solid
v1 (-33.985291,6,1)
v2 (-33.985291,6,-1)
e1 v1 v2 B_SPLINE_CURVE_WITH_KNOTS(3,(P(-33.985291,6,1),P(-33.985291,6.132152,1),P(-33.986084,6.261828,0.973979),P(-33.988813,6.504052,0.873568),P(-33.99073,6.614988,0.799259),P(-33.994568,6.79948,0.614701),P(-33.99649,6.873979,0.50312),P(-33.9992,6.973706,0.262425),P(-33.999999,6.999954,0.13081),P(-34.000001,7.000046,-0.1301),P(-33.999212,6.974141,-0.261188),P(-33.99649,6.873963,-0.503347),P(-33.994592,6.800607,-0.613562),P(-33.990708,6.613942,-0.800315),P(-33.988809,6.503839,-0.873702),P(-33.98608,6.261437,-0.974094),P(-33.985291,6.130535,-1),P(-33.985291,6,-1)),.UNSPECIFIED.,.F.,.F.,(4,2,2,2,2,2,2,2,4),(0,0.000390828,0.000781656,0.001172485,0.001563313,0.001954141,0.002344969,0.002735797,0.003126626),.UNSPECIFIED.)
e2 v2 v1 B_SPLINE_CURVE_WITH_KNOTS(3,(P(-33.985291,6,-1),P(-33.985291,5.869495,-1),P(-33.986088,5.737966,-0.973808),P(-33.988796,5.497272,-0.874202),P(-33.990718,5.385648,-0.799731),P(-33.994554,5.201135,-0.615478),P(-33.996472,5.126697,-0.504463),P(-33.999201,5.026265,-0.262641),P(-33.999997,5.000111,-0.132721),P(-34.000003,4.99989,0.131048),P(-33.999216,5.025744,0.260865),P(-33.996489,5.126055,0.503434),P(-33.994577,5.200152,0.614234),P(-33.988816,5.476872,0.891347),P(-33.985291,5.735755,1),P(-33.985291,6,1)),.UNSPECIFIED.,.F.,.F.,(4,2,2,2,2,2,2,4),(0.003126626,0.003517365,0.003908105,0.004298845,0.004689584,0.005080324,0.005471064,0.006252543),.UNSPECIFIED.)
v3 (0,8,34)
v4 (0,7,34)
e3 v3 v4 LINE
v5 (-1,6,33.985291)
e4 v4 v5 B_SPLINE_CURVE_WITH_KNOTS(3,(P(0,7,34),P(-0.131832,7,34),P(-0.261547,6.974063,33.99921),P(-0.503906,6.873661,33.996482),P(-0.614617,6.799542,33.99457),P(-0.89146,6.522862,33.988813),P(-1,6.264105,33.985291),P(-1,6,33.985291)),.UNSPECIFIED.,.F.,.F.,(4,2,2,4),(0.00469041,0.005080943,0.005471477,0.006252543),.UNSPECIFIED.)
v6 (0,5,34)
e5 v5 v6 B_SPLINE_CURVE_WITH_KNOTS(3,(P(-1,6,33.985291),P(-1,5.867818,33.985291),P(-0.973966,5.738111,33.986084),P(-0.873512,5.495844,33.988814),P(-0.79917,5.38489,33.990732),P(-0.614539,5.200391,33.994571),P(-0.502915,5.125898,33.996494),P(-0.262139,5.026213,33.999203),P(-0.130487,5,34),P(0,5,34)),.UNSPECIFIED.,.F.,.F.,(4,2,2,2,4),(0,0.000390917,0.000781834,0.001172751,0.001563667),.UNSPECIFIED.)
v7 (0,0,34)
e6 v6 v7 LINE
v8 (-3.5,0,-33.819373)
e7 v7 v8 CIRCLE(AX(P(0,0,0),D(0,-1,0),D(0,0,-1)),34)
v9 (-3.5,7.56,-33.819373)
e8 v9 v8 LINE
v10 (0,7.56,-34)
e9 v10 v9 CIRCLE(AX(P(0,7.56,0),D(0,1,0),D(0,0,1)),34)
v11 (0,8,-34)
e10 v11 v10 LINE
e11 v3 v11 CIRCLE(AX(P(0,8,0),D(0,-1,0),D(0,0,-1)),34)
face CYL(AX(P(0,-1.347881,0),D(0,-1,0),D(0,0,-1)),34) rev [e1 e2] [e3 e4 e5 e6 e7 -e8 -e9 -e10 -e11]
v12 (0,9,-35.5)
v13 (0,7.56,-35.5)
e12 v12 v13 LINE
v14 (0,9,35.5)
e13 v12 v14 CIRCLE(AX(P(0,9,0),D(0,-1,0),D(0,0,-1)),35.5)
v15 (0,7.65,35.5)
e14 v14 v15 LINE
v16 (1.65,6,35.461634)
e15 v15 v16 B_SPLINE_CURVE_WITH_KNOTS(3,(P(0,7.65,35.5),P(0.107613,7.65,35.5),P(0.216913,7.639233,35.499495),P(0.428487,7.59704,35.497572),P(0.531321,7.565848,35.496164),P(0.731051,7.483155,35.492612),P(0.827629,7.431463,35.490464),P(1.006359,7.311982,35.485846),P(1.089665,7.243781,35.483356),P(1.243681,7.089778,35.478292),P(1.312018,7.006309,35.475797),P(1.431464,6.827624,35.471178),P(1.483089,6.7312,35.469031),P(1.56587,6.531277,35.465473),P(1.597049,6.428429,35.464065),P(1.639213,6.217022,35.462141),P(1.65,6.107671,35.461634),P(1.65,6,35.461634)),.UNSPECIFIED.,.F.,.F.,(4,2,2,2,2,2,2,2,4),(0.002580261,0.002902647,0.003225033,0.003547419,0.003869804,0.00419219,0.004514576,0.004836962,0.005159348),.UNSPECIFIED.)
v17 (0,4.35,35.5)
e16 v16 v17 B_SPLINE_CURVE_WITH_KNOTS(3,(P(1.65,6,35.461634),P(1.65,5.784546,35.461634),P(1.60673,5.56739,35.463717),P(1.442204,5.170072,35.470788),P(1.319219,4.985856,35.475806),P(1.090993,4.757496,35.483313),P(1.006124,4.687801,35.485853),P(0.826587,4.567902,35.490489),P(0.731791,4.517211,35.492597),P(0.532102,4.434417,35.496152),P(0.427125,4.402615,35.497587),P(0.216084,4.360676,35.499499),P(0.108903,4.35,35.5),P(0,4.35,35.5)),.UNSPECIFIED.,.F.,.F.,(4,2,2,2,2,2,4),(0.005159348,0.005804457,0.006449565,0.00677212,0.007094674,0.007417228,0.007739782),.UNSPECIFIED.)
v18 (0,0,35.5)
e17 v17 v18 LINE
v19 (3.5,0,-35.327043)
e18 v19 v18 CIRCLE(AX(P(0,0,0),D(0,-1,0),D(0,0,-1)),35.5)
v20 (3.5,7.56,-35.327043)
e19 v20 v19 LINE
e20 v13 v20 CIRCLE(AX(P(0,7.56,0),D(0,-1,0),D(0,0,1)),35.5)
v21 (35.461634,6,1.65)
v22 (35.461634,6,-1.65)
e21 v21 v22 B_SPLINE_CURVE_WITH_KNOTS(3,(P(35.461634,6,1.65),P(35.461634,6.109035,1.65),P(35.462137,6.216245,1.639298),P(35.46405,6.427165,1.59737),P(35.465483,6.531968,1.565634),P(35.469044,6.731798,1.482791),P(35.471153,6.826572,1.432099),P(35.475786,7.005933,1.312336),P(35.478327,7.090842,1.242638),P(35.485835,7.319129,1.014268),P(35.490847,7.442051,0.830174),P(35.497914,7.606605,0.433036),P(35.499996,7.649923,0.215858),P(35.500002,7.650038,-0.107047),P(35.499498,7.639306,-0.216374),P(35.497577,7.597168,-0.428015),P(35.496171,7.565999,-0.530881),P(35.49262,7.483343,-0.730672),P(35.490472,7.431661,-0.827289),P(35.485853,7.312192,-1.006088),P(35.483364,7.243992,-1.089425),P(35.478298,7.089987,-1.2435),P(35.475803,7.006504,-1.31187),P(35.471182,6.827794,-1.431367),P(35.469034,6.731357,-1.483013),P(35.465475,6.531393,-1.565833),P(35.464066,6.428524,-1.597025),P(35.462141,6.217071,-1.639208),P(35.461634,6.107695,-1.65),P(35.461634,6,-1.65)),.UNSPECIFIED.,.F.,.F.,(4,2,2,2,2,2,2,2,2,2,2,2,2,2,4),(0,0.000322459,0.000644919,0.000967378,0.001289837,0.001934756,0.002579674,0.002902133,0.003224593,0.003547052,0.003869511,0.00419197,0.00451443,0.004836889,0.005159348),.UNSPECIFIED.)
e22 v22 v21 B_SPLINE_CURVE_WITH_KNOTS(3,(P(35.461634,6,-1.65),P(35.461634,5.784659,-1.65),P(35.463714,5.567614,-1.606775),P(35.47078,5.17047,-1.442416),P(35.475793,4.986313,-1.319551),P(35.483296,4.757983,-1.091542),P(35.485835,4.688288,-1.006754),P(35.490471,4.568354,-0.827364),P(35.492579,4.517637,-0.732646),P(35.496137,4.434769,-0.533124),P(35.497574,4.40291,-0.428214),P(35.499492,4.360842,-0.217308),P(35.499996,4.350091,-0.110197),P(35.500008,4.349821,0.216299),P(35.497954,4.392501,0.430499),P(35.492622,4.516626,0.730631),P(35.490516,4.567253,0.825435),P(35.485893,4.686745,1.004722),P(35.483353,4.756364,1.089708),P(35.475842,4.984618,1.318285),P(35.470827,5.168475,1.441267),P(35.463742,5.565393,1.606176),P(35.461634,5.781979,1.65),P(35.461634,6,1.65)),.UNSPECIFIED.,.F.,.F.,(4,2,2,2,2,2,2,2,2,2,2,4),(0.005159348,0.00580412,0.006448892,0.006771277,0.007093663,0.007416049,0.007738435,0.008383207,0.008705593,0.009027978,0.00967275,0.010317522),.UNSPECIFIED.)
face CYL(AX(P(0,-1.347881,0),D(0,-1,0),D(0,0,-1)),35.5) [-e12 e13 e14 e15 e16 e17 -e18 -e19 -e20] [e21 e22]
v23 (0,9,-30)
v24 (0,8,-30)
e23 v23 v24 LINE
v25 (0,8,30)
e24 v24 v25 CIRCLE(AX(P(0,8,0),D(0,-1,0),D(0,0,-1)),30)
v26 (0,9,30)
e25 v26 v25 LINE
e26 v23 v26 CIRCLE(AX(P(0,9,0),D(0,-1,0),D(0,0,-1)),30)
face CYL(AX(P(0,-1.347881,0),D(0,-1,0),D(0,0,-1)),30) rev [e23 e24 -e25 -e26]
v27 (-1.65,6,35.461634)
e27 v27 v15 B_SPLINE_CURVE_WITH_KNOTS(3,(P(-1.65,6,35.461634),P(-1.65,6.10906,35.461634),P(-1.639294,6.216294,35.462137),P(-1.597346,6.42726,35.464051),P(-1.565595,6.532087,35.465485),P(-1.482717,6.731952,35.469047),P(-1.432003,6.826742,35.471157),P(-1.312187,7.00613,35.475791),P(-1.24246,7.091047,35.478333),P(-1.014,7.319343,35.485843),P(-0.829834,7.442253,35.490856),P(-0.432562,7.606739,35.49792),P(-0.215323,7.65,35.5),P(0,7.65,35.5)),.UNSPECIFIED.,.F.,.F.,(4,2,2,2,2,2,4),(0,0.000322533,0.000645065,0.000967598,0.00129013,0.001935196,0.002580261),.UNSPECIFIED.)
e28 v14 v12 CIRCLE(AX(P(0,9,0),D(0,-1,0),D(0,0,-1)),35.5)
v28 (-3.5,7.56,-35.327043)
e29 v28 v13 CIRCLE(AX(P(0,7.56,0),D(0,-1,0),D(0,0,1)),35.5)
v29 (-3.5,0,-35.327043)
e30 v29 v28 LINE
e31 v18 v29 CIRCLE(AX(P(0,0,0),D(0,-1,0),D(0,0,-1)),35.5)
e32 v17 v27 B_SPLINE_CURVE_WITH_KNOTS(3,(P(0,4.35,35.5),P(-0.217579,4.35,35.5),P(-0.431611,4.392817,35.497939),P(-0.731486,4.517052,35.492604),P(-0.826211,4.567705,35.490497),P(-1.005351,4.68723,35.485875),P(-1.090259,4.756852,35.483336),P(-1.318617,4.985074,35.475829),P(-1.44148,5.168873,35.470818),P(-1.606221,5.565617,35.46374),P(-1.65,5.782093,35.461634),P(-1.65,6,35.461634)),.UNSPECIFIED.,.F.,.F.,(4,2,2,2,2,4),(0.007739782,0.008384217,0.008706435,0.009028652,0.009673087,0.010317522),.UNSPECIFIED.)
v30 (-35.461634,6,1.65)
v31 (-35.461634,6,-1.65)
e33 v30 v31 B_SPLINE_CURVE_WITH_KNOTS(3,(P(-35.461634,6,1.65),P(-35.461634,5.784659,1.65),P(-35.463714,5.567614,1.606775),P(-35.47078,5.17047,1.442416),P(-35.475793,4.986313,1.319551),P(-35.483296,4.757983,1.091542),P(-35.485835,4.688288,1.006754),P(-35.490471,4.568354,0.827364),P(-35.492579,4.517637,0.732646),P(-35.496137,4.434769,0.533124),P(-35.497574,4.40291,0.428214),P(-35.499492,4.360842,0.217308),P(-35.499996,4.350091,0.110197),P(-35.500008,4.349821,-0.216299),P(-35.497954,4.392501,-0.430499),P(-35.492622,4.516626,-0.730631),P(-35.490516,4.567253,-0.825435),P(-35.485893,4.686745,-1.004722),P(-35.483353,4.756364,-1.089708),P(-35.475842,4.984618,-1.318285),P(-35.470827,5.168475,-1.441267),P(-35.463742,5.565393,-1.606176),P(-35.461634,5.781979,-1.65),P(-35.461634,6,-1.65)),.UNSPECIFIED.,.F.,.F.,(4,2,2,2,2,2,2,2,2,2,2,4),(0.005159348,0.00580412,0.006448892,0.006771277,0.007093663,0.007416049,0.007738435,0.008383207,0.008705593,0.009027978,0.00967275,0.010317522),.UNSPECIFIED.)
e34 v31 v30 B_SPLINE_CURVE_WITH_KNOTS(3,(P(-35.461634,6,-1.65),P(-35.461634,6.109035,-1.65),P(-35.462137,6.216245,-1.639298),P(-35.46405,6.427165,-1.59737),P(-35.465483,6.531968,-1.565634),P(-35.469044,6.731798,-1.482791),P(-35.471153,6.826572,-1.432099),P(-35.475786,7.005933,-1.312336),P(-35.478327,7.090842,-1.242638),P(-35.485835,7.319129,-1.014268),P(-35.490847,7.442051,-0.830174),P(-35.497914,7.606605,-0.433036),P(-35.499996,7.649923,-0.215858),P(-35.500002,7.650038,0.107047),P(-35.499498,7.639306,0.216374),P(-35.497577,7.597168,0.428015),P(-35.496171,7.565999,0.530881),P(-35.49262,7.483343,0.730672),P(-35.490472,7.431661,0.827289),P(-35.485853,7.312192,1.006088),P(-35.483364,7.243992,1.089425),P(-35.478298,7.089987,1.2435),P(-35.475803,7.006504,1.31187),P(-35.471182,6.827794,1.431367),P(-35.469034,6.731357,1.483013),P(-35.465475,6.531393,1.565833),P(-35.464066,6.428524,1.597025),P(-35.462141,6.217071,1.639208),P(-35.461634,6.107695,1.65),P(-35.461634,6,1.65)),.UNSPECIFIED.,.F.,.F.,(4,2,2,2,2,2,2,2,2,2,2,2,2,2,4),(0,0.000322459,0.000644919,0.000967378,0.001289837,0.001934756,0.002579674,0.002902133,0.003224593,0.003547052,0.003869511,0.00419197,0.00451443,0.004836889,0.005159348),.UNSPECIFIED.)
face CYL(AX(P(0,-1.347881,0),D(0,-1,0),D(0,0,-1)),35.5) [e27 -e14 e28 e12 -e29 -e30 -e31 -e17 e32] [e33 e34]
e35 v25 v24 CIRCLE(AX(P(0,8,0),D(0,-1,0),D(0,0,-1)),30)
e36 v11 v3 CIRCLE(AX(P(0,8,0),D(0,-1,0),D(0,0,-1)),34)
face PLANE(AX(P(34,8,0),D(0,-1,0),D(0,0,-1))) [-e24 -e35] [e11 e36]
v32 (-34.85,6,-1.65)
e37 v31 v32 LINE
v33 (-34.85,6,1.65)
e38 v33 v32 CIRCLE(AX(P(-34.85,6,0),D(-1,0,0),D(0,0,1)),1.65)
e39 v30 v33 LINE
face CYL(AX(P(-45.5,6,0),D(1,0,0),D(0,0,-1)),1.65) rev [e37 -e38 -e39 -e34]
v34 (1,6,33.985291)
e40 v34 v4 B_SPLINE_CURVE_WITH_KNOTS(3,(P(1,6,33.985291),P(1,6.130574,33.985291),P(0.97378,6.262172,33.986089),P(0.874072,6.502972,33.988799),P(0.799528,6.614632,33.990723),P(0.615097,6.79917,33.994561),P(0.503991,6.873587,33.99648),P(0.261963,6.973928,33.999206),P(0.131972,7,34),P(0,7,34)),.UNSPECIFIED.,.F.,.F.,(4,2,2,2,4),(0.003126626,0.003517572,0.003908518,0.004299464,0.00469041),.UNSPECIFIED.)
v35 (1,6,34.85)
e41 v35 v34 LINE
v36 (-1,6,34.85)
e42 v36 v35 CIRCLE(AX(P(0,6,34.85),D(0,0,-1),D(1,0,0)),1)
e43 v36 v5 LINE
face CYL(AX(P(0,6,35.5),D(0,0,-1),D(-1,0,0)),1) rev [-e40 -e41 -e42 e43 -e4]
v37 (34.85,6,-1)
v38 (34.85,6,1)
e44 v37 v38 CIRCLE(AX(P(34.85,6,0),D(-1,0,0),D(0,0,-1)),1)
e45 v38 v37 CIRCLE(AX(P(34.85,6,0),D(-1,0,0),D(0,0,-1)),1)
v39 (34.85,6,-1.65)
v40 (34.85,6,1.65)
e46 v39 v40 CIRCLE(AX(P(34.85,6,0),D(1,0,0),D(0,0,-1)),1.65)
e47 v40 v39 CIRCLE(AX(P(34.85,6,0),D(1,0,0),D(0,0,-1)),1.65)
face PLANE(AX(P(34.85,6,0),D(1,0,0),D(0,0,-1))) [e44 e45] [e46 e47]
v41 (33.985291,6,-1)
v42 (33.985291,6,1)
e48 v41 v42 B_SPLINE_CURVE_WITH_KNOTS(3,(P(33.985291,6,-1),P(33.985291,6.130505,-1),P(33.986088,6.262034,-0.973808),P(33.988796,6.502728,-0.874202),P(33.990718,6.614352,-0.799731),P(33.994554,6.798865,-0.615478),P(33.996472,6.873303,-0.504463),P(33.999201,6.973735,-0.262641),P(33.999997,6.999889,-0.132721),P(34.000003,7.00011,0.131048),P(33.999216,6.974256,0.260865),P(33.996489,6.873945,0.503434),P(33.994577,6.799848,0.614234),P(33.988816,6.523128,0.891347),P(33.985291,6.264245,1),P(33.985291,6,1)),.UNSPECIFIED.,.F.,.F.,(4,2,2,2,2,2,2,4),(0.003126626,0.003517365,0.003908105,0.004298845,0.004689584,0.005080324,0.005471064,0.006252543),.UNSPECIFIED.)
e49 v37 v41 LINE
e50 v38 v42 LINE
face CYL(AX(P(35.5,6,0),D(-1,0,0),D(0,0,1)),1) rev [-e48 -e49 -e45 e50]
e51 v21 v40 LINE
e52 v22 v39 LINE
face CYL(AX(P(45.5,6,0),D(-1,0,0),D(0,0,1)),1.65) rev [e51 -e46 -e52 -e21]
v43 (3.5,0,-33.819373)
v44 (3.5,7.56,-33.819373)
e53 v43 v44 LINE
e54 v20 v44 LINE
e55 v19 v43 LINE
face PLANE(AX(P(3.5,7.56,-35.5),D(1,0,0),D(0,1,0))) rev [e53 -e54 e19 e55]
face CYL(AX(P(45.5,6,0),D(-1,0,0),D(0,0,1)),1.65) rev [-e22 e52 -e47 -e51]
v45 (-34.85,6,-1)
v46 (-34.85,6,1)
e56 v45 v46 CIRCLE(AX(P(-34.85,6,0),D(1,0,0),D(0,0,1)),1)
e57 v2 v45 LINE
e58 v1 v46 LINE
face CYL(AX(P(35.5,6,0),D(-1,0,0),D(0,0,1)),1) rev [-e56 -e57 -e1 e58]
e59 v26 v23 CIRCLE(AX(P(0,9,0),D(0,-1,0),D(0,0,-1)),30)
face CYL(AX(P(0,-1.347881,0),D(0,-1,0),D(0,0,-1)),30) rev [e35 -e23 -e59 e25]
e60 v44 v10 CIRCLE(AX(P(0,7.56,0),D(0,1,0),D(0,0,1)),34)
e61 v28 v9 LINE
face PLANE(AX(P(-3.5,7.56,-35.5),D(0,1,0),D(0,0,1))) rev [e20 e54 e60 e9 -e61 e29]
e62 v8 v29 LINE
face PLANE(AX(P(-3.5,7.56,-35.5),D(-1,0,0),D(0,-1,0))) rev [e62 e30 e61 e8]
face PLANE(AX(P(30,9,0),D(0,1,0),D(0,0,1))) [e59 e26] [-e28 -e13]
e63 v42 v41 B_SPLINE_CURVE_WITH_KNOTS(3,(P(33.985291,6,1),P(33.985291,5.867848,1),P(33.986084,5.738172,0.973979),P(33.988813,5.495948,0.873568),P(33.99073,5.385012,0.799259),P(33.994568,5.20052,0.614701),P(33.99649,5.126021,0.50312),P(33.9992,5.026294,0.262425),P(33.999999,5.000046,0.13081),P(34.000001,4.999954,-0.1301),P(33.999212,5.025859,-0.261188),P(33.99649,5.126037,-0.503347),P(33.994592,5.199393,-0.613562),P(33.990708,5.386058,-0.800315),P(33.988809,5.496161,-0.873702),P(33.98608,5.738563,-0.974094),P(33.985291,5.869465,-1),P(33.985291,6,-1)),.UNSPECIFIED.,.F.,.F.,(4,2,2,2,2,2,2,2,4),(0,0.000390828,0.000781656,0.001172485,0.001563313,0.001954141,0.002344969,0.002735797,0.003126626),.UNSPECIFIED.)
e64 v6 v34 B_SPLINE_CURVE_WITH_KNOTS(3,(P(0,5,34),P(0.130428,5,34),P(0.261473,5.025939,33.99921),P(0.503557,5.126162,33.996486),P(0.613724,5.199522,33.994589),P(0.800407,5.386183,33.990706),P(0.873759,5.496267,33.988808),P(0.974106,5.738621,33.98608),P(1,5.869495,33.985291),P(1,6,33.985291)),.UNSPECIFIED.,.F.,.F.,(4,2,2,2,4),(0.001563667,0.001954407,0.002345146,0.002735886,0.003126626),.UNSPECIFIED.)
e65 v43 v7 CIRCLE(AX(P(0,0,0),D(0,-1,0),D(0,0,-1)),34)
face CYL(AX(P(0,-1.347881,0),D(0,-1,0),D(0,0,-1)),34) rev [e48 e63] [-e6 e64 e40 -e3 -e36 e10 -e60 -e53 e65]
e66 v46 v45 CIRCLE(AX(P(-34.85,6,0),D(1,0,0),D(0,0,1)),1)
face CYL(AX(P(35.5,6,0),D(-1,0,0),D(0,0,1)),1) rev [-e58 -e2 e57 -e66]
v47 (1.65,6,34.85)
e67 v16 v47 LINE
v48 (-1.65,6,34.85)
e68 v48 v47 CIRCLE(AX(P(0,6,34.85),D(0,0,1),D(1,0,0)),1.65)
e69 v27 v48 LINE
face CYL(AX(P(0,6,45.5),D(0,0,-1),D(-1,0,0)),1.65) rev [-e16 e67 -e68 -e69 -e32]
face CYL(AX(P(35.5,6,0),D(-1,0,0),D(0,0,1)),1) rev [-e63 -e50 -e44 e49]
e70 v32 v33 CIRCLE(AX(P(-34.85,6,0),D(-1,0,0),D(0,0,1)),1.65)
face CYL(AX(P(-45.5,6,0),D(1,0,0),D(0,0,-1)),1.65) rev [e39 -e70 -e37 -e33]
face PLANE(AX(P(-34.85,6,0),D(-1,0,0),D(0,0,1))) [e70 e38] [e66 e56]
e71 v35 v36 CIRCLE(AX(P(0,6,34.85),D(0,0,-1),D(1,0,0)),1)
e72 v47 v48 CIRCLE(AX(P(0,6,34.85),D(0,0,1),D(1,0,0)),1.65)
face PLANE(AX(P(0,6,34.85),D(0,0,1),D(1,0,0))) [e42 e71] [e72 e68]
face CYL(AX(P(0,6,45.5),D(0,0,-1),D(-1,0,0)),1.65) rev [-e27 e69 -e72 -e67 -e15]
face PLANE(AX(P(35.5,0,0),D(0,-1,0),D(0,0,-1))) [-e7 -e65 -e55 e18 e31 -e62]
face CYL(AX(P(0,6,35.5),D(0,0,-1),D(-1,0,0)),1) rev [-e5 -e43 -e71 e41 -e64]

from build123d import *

# Parameters (mm, degrees)
SKETCH2_W          = 7
SKETCH2_H          = 10
CUT_EXTRUDE1_DEPTH = 52.004901725
CUT_EXTRUDE2_START = 34.85
SKETCH3_R          = 1.65
CUT_EXTRUDE2_DEPTH = 10.65
CIRPATTERN1_COUNT  = 4
SKETCH4_R          = 1
CUT_EXTRUDE3_DEPTH = 52.004901895
CIRPATTERN3_COUNT  = 4


with BuildPart() as part:
    # Sketch1 → Revolve1 (revolve)
    with BuildSketch(Plane.XY, mode=Mode.PRIVATE) as revolve1_sk:
        Polygon((34, 0), (34, 8), (30, 8), (30, 9), (35.5, 9), (35.5, 0), align=None)
    revolve(revolve1_sk.sketch.rotate(Axis((0, -1.347881032, 0), (0, 1, 0)), 90), axis=Axis((0, -1.347881032, 0), (0, 1, 0)))

    # Sketch2 → Cut-Extrude1 (cut, through all)
    with BuildSketch(Plane.XY):
        with Locations((0, 2.56)):
            Rectangle(SKETCH2_W, SKETCH2_H)
    extrude(amount=-CUT_EXTRUDE1_DEPTH, mode=Mode.SUBTRACT)

    # Sketch3 → Cut-Extrude2 (cut)
    with BuildSketch(Plane.XY.offset(CUT_EXTRUDE2_START)):
        with Locations(Location((0, 6, 0), (0, 0, 180))):
            Circle(SKETCH3_R)
    cut_extrude2 = extrude(amount=CUT_EXTRUDE2_DEPTH, mode=Mode.SUBTRACT)

    # CirPattern1: Cut-Extrude2 ×4 about axis, 1 skipped
    cirpattern1_axis = Axis((0, 0, 0), (0, -1, 0))
    add([cut_extrude2.rotate(cirpattern1_axis, i * 360 / CIRPATTERN1_COUNT) for i in range(1, CIRPATTERN1_COUNT) if i not in (2,)], mode=Mode.SUBTRACT)

    # Sketch4 → Cut-Extrude3 (cut, through all)
    with BuildSketch(Plane.XY):
        with Locations(Location((0, 6, 0), (0, 0, 180))):
            Circle(SKETCH4_R)
    cut_extrude3 = extrude(amount=CUT_EXTRUDE3_DEPTH, mode=Mode.SUBTRACT)

    # CirPattern3: Cut-Extrude3 ×4 about axis, 1 skipped
    cirpattern3_axis = Axis((0, -1.347881032, 0), (0, -1, 0))
    add([cut_extrude3.rotate(cirpattern3_axis, i * 360 / CIRPATTERN3_COUNT) for i in range(1, CIRPATTERN3_COUNT) if i not in (2,)], mode=Mode.SUBTRACT)


solid = part.part
